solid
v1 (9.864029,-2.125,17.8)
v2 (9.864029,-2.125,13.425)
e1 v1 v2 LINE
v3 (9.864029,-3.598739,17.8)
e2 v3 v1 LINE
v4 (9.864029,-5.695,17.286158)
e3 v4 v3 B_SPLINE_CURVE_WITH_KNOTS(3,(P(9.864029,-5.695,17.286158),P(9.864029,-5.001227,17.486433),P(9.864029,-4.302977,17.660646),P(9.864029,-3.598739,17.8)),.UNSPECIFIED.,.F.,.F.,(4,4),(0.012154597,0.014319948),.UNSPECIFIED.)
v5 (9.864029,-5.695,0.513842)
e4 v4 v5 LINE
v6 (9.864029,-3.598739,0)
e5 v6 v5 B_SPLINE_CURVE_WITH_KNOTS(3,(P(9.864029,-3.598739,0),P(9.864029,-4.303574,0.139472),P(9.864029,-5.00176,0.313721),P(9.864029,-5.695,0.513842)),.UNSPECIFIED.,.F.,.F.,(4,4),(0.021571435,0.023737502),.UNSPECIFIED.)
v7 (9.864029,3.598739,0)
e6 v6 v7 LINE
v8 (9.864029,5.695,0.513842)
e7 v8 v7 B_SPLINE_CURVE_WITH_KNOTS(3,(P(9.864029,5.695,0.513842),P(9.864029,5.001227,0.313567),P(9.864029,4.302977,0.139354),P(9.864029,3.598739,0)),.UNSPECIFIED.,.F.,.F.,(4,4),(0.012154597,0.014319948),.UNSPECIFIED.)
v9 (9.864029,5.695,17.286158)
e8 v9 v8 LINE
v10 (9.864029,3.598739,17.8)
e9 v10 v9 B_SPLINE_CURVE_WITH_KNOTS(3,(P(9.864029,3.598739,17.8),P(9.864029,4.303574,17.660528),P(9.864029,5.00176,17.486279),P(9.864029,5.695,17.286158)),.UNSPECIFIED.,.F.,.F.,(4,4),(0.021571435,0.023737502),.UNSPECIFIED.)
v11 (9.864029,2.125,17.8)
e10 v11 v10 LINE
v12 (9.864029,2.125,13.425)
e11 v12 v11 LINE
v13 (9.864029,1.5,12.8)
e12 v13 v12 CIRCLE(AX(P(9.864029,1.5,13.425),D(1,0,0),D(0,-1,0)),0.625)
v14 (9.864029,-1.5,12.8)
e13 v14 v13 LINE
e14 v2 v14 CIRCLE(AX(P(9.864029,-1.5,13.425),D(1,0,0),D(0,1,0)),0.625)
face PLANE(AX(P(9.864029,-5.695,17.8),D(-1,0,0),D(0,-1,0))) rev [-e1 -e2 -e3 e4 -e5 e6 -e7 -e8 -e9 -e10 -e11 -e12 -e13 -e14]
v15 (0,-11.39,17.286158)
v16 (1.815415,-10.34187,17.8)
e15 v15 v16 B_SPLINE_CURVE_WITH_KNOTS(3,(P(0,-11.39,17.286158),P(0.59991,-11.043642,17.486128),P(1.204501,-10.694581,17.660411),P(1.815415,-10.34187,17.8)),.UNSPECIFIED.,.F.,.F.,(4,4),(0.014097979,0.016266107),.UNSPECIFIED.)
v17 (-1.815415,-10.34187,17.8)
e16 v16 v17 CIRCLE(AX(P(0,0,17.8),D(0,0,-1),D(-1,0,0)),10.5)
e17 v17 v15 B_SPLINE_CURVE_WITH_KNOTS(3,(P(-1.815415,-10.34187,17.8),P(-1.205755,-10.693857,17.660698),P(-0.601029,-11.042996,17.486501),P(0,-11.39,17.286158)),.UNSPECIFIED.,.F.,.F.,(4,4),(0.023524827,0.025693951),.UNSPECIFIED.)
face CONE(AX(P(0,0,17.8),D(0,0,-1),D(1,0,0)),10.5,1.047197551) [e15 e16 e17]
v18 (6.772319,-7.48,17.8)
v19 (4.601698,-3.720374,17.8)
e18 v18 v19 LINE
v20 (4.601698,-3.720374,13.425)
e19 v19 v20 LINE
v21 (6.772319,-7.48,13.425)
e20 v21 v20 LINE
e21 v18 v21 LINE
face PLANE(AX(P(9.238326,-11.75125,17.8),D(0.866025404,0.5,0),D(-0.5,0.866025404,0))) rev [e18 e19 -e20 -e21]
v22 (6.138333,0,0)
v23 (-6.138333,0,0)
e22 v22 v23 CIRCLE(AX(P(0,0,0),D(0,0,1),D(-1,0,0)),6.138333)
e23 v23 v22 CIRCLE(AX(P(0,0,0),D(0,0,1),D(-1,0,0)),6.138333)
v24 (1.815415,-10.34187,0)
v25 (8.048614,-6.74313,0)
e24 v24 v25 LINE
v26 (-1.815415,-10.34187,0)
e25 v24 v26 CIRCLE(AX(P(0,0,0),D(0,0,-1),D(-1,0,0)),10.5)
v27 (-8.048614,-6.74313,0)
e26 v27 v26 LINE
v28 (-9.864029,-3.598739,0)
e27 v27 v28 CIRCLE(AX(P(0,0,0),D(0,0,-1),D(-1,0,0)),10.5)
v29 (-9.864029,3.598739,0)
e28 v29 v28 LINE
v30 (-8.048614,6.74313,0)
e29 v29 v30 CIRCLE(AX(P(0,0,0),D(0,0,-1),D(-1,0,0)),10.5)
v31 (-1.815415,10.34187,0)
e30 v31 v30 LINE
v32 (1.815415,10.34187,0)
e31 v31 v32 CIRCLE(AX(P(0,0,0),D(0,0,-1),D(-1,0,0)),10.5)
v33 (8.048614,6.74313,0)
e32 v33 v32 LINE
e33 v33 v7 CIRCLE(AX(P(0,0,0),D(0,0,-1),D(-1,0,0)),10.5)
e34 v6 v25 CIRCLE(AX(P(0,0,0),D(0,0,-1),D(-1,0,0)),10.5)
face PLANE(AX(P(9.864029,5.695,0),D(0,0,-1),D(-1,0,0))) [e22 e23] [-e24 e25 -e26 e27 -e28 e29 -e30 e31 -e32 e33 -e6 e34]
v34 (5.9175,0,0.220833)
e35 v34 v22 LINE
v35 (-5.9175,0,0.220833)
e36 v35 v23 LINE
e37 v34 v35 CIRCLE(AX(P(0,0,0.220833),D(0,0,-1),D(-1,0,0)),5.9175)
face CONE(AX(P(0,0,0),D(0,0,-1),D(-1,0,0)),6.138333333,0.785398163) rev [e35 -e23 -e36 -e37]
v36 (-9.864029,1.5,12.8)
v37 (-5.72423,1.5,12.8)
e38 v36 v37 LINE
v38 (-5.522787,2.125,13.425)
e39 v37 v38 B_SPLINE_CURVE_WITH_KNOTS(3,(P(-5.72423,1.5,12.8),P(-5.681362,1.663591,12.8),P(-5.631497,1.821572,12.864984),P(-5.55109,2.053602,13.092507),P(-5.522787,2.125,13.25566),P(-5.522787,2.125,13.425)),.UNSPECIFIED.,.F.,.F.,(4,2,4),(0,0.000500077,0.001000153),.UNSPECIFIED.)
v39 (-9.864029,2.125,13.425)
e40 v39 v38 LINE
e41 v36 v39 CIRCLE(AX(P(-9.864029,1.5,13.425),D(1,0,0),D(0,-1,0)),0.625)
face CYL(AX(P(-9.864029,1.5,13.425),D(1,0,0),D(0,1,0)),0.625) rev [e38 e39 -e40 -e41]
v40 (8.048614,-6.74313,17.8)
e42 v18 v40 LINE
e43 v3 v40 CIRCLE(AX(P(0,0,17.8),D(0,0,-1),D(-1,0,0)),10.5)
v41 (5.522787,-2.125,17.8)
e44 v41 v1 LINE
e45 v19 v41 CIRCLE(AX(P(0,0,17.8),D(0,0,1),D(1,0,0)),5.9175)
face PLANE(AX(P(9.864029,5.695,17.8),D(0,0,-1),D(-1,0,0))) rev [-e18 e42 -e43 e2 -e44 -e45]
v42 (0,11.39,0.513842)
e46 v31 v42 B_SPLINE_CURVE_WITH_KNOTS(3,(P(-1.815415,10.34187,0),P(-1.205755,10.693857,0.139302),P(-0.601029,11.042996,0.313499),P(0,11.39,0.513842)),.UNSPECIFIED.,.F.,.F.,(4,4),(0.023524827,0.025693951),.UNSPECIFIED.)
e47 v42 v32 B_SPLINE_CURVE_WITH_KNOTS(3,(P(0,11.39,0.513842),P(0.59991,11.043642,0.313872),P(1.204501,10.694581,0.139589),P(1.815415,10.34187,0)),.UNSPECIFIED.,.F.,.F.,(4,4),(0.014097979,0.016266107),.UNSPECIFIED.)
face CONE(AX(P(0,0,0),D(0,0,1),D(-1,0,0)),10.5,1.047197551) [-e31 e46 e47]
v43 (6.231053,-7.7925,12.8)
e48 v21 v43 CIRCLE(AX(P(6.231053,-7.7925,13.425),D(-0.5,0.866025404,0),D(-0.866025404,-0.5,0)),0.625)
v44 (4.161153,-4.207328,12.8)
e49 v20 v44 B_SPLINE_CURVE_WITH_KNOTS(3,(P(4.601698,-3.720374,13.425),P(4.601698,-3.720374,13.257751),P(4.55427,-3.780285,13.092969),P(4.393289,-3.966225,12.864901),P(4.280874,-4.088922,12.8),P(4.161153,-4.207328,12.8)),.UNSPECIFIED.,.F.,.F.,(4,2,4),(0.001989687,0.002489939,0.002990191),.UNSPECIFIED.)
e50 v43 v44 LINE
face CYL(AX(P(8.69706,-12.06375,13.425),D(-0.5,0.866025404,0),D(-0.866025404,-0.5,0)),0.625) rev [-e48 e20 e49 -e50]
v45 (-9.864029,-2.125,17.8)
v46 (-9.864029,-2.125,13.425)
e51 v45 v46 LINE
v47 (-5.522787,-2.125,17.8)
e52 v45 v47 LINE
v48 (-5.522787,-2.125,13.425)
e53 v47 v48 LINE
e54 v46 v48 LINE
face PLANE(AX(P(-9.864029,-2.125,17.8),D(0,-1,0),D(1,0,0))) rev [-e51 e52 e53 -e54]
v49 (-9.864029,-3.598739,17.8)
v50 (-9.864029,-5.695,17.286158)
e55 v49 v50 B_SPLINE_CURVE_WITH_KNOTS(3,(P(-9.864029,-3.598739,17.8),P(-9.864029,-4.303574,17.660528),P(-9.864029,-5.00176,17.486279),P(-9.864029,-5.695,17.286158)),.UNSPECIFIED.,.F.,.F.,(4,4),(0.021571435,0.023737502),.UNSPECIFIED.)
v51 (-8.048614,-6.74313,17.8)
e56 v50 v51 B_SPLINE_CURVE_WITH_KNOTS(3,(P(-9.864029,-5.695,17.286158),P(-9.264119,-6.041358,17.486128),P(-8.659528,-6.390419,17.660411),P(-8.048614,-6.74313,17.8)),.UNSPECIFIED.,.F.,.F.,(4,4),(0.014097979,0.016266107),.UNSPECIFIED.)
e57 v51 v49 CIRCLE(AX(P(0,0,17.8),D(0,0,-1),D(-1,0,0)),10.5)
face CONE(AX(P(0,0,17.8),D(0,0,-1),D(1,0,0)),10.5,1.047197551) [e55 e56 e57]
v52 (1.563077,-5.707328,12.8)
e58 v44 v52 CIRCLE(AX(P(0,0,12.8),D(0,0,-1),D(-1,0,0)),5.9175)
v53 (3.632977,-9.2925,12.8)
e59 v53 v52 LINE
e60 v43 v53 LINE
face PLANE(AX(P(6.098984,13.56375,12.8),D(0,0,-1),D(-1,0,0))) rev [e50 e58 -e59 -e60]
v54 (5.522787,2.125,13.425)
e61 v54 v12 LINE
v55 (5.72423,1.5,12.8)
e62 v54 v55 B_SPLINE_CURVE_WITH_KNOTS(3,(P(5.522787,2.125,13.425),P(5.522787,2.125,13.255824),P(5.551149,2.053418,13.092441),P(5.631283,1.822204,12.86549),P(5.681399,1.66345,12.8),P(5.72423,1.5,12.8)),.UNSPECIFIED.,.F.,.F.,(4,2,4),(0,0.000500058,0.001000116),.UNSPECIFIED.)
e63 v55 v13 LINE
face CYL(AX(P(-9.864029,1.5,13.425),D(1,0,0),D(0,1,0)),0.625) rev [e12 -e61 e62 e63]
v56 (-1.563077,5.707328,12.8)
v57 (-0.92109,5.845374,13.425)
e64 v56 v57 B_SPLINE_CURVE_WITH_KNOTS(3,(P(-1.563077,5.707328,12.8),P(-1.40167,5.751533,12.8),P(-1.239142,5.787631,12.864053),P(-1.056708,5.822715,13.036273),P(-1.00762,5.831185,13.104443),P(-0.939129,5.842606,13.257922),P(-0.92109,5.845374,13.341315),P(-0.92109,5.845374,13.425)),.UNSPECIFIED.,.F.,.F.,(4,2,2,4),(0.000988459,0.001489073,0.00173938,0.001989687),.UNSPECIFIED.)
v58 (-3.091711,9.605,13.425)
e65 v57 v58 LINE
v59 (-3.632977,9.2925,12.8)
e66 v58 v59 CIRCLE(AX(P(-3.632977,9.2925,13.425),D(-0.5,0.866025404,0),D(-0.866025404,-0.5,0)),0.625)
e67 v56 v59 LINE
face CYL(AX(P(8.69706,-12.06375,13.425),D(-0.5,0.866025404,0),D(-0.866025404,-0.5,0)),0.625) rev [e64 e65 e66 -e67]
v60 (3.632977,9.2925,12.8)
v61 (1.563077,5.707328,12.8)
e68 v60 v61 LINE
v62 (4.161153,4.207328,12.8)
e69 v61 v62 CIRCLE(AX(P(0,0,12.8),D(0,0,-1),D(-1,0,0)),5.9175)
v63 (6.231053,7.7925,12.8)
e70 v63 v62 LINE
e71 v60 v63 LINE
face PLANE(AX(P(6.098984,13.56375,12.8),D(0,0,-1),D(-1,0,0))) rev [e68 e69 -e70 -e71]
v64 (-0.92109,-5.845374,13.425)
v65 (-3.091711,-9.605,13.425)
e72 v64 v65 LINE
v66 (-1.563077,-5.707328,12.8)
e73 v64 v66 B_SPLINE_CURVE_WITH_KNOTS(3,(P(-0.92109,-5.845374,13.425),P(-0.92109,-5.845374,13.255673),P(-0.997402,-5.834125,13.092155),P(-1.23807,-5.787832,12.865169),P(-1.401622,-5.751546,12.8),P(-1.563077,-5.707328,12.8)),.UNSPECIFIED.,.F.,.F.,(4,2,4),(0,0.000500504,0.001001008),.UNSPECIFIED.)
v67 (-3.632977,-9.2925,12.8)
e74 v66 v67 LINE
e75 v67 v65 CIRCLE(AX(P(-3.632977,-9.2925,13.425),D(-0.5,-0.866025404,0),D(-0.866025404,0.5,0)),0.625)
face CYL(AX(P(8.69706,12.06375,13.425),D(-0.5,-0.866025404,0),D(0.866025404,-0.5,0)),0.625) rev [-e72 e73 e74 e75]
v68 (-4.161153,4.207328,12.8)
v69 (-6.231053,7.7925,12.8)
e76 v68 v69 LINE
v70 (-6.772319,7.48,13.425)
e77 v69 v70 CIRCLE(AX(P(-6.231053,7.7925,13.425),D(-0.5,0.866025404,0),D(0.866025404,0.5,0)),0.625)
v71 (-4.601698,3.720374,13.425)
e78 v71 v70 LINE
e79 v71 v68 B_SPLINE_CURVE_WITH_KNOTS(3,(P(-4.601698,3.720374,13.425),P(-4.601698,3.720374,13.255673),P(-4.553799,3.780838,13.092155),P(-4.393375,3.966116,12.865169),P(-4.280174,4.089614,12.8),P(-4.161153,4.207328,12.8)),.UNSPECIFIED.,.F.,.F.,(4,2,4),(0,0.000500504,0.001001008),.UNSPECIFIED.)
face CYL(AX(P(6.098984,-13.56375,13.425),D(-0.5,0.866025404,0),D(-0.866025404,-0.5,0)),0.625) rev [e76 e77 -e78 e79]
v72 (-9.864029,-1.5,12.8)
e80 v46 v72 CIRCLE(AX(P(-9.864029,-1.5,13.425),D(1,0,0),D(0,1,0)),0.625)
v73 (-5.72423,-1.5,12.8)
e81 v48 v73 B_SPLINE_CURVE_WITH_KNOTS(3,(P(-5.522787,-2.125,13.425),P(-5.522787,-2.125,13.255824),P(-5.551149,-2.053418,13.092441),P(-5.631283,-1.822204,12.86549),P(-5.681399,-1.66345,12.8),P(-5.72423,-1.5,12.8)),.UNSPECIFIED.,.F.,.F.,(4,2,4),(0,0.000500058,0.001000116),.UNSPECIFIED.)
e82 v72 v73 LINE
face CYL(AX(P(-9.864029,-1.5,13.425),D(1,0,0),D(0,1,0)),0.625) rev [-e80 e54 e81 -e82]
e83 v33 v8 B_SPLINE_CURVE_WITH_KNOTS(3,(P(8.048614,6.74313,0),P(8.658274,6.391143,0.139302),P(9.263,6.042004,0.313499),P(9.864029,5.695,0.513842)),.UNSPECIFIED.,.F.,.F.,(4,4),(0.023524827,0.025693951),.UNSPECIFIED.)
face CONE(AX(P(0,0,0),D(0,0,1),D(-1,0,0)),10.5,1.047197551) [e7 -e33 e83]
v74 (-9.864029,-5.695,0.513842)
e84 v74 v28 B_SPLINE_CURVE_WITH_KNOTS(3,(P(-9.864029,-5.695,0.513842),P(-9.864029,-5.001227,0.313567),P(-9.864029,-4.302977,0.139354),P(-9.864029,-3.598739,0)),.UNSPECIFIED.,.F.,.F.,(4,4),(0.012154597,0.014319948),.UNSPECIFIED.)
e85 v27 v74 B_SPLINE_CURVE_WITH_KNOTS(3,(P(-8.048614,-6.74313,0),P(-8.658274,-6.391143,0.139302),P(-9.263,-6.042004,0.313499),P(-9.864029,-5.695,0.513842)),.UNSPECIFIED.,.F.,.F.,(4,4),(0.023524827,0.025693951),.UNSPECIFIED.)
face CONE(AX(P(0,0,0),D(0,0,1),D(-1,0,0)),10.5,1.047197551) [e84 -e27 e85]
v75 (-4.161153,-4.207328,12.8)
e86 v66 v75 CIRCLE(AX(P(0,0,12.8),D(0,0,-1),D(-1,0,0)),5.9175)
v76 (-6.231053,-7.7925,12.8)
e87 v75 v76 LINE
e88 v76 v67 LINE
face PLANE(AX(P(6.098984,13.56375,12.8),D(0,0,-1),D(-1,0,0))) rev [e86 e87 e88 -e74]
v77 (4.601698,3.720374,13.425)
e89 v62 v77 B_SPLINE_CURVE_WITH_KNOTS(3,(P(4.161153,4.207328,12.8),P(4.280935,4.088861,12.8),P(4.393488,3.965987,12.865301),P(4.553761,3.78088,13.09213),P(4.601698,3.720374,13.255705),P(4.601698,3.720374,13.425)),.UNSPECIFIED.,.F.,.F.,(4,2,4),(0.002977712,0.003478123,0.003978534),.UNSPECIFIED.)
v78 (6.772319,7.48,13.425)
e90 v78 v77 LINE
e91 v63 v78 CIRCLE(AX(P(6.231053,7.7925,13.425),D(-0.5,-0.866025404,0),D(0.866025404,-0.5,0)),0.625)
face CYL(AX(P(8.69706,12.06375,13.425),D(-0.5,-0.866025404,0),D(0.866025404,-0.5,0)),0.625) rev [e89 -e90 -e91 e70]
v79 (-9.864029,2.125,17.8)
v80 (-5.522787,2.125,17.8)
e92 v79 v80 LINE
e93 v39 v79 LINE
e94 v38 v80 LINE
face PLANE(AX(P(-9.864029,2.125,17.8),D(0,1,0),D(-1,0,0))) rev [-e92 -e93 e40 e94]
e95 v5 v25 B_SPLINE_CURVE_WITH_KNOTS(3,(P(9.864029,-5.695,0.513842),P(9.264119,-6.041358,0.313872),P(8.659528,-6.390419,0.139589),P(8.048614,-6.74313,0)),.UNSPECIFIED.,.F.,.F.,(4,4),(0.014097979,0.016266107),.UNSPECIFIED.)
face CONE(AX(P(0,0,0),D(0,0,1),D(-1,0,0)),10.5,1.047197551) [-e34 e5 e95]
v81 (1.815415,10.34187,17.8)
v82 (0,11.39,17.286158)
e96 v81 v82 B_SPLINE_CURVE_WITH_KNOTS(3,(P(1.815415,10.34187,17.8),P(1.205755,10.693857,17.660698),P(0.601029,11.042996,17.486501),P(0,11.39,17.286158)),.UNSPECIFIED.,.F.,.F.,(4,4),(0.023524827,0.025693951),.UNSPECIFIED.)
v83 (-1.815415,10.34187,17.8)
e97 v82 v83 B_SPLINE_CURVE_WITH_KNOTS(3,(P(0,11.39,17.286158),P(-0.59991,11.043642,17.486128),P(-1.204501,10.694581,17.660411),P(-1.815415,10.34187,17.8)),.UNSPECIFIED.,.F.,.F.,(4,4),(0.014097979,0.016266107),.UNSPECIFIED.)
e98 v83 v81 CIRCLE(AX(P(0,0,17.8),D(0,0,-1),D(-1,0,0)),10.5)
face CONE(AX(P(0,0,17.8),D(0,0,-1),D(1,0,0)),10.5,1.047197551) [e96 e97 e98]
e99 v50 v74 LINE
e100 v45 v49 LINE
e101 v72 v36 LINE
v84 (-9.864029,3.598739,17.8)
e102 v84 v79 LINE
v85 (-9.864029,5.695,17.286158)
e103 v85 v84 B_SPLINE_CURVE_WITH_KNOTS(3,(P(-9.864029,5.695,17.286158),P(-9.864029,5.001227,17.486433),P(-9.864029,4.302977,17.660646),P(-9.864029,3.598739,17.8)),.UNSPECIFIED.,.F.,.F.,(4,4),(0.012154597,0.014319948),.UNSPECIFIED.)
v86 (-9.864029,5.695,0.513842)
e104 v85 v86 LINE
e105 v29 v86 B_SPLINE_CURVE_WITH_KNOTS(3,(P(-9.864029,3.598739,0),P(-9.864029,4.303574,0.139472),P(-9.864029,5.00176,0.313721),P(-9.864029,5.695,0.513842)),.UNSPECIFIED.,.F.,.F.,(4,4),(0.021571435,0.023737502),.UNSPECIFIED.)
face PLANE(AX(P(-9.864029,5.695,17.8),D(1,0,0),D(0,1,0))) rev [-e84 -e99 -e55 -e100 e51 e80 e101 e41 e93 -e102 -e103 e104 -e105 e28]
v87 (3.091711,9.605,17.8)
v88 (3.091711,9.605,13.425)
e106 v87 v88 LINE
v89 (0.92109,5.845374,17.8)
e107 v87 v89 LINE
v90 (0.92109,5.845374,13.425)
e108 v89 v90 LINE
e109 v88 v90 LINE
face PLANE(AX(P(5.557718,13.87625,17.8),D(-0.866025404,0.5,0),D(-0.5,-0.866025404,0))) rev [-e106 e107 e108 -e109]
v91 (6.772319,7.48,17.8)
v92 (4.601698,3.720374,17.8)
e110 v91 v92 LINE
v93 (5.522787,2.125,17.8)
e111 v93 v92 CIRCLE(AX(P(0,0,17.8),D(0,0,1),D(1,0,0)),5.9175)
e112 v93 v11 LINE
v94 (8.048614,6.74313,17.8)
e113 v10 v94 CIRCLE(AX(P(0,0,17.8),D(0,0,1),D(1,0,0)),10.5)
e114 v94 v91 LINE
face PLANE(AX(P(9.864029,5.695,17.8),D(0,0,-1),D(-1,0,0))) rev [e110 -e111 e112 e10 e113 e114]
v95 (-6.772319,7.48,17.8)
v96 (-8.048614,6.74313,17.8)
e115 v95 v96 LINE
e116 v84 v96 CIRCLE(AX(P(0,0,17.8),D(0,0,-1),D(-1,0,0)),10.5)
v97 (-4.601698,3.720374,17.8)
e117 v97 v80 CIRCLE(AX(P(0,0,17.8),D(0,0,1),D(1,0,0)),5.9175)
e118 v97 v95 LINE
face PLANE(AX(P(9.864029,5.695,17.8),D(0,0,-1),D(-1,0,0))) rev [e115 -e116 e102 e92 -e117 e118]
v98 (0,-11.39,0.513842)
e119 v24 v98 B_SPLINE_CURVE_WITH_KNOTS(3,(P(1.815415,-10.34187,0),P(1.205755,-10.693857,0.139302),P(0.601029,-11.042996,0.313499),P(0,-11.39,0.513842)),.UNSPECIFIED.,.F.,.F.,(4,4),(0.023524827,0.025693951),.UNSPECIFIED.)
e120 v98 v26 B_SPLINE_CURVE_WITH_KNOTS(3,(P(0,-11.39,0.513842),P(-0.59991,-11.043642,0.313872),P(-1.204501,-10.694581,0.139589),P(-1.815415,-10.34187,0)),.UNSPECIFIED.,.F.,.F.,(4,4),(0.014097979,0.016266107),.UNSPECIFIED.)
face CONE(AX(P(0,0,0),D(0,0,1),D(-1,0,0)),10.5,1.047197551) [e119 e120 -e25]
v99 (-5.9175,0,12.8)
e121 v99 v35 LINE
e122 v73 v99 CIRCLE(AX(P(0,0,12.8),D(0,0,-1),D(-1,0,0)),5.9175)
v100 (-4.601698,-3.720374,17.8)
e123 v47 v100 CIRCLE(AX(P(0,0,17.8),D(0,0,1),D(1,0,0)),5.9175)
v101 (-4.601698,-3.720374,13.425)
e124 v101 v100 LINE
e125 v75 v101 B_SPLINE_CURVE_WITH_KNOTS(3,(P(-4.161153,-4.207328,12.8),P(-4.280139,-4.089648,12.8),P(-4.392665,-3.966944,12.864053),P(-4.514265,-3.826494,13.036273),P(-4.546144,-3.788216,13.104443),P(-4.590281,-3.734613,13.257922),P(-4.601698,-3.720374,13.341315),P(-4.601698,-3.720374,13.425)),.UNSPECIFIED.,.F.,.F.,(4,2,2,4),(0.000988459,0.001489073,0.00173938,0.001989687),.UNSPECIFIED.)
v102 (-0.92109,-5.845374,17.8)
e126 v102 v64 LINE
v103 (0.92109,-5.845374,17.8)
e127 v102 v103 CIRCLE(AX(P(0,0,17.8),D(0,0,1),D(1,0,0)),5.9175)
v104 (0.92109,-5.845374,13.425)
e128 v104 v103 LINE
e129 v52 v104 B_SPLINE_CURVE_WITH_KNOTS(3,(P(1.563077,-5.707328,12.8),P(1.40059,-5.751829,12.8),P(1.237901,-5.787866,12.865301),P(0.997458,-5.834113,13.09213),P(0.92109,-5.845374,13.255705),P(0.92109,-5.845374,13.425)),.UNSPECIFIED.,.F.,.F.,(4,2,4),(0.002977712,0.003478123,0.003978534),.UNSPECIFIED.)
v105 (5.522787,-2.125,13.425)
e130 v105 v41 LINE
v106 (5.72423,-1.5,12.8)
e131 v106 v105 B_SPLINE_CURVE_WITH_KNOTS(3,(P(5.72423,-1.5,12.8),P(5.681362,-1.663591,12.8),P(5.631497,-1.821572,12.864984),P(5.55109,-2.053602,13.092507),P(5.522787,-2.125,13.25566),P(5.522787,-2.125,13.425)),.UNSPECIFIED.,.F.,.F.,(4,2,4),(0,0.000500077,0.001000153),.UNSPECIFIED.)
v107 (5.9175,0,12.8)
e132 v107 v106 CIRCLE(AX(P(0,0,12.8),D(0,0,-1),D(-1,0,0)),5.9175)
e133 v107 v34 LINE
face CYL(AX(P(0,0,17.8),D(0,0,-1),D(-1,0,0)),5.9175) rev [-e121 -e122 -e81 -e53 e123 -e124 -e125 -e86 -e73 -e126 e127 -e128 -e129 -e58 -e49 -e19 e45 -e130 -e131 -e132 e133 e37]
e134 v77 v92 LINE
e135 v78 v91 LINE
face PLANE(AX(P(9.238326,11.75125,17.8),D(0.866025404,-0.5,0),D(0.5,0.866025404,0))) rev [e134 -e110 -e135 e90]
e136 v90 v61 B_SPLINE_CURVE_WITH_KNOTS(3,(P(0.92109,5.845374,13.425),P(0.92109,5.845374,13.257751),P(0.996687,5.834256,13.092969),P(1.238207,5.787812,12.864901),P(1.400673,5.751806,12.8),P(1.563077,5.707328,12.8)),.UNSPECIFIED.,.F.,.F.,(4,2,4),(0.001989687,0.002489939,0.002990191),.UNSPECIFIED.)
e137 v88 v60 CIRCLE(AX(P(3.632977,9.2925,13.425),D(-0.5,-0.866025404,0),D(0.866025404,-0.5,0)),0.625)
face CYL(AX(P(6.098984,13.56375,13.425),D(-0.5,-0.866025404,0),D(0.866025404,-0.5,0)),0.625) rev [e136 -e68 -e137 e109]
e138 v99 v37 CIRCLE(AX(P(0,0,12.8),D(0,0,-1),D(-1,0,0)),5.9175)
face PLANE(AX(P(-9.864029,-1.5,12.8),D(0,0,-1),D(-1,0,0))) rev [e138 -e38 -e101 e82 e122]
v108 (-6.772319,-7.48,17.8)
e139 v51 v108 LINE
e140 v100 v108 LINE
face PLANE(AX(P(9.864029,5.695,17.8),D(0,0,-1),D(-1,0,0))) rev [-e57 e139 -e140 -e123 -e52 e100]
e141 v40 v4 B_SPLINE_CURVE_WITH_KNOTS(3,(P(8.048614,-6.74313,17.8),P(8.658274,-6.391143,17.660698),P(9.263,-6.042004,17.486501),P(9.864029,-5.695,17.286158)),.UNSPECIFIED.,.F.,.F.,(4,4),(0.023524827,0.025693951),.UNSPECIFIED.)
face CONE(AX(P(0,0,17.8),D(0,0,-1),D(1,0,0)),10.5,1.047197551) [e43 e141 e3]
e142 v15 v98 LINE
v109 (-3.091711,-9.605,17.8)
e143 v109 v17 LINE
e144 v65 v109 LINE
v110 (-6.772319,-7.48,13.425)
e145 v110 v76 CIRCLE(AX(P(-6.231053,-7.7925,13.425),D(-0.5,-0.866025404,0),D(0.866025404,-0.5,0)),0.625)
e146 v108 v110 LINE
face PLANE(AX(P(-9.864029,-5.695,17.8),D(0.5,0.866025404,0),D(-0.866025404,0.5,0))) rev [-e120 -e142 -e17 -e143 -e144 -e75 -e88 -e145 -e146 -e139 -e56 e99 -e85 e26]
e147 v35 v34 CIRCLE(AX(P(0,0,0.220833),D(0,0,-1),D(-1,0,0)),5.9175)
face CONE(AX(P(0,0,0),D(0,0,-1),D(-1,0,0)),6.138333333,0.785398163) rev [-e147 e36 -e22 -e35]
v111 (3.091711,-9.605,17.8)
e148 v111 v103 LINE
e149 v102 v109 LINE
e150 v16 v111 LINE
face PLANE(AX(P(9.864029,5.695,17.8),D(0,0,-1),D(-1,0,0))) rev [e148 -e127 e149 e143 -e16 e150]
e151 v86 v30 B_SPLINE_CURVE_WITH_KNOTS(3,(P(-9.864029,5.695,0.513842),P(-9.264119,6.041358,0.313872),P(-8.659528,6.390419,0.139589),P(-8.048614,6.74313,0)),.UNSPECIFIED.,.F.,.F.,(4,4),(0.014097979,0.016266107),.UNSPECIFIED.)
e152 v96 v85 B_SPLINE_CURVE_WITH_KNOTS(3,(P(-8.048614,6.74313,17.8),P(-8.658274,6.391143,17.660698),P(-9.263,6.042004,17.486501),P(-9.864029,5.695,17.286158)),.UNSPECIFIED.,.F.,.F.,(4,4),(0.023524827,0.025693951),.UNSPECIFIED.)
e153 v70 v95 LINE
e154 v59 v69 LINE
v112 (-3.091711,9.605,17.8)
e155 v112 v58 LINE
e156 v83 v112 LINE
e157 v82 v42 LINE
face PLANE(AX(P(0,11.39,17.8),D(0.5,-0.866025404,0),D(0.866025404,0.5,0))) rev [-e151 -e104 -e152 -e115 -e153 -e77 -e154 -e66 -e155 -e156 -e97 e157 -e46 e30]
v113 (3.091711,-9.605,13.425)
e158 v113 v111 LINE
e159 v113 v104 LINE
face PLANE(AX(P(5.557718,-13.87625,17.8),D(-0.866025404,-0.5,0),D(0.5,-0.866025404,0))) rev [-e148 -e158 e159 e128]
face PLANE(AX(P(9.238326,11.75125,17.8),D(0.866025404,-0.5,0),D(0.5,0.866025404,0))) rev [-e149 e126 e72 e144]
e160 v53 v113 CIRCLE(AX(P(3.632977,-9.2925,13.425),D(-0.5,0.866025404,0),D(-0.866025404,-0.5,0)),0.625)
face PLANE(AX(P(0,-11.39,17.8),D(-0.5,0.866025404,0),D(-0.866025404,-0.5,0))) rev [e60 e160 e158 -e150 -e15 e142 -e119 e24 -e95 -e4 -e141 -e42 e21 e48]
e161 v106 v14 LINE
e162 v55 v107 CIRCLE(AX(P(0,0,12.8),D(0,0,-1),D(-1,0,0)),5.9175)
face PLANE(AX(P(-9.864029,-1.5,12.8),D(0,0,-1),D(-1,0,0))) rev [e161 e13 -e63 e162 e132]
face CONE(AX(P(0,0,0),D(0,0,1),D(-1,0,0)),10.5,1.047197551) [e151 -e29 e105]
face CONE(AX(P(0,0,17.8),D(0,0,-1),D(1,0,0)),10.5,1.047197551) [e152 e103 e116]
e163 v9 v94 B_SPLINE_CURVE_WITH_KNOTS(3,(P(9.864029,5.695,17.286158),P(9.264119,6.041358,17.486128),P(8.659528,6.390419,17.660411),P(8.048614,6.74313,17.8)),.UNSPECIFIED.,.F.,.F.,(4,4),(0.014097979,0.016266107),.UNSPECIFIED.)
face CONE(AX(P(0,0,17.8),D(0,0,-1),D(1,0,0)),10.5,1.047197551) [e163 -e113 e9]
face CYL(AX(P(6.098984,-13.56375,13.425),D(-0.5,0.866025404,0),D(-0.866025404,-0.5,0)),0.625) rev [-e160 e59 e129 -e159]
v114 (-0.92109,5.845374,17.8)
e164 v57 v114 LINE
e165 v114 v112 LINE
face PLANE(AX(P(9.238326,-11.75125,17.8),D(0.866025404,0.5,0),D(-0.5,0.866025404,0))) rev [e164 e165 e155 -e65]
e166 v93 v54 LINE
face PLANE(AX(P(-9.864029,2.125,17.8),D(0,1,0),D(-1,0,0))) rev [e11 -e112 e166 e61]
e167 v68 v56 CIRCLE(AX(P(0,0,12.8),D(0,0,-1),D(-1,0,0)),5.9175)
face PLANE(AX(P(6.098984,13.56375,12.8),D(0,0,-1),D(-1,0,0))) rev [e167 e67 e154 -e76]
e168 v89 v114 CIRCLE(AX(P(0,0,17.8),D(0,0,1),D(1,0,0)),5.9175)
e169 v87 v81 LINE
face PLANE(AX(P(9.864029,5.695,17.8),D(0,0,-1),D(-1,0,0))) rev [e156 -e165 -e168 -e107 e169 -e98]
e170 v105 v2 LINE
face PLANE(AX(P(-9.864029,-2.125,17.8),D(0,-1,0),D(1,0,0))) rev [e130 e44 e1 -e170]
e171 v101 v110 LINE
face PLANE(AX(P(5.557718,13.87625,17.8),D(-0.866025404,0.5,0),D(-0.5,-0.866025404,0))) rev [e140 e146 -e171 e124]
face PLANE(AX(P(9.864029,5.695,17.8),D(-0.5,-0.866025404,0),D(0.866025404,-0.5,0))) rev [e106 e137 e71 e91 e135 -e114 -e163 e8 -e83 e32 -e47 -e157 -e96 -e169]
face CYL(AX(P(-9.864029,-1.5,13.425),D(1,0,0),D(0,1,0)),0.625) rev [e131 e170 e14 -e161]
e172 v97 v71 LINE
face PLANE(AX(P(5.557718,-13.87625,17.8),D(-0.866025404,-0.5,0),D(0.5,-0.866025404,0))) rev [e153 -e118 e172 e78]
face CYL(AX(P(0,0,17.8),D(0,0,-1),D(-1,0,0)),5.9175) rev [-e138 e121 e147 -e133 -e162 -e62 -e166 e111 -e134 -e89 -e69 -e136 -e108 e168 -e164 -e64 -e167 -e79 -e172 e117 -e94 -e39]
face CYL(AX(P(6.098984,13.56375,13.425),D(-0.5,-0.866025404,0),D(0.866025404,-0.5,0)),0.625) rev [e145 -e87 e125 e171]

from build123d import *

# Parameters (mm, degrees)
SKETCH1_R          = 5.9175
BASE_EXTRUDE_DEPTH = 17.8
SKETCH2_OUTSIDE_W  = 112.978
SKETCH2_OUTSIDE_H  = 116.03
SKETCH2_OUTSIDE_R  = 10.5
CUT_EXTRUDE1_DEPTH = 24.321045753
CUT_EXTRUDE1_DRAFT = -60
SKETCH3_OUTSIDE_W  = 112.978
SKETCH3_OUTSIDE_H  = 116.03
SKETCH3_OUTSIDE_R  = 10.5
CUT_EXTRUDE2_DEPTH = 24.321045753
CUT_EXTRUDE2_DRAFT = -60
CUT_EXTRUDE3_DEPTH = 29.909659285
CIRPATTERN1_COUNT  = 3
CHAMFER1_SIZE      = 0.220833333


with BuildPart() as part:
    # Sketch1 → Base-Extrude (new body)
    with BuildSketch(Plane.XY):
        Polygon((0, 11.39), (-9.864029349, 5.695), (-9.864029349, -5.695), (0, -11.39), (9.864029349, -5.695), (9.864029349, 5.695), align=None)
        Circle(SKETCH1_R, mode=Mode.SUBTRACT)
    extrude(amount=BASE_EXTRUDE_DEPTH)


with BuildPart() as cut_extrude1_tool:
    # Sketch2 outside → Cut-Extrude1 (with draft: the straight prism first)
    with BuildSketch(Plane(origin=(0, 0, 0), x_dir=(-1, 0, 0), z_dir=(0, 0, -1))):
        Rectangle(SKETCH2_OUTSIDE_W, SKETCH2_OUTSIDE_H)
        Circle(SKETCH2_OUTSIDE_R, mode=Mode.SUBTRACT)
    extrude(amount=-CUT_EXTRUDE1_DEPTH)
    # Cut-Extrude1: the draft: its side faces are tilted about the plane it starts from
    cut_extrude1_sides = [cut_extrude1_tool.faces().sort_by_distance(p)[0] for p in [
        (0, -58.015, 12.160522876),
        (-56.489, 0, 12.160522876),
        (0, 58.015, 12.160522876),
        (56.489, 0, 12.160522876),
        (10.5, 0, 12.160522876),
    ]]
    draft(cut_extrude1_sides, Plane(origin=(0, 0, 0), x_dir=(-1, 0, 0), z_dir=(0, 0, -1)), CUT_EXTRUDE1_DRAFT)


with BuildPart() as part_1:
    add(part.part)

    # Cut-Extrude1: cut by cut_extrude1_tool
    add(cut_extrude1_tool.part, mode=Mode.SUBTRACT)


with BuildPart() as cut_extrude2_tool:
    # Sketch3 outside → Cut-Extrude2 (with draft: the straight prism first)
    with BuildSketch(Plane.XY.offset(17.8)):
        Rectangle(SKETCH3_OUTSIDE_W, SKETCH3_OUTSIDE_H)
        Circle(SKETCH3_OUTSIDE_R, mode=Mode.SUBTRACT)
    extrude(amount=-CUT_EXTRUDE2_DEPTH)
    # Cut-Extrude2: the draft: its side faces are tilted about the plane it starts from
    cut_extrude2_sides = [cut_extrude2_tool.faces().sort_by_distance(p)[0] for p in [
        (0, -58.015, 5.639477124),
        (56.489, 0, 5.639477124),
        (0, 58.015, 5.639477124),
        (-56.489, 0, 5.639477124),
        (-10.5, 0, 5.639477124),
    ]]
    draft(cut_extrude2_sides, Plane.XY.offset(17.8), CUT_EXTRUDE2_DRAFT)


with BuildPart() as part_2:
    add(part_1.part)

    # Cut-Extrude2: cut by cut_extrude2_tool
    add(cut_extrude2_tool.part, mode=Mode.SUBTRACT)

    # Sketch6 → Cut-Extrude3 (cut, through all)
    with BuildSketch(Plane(origin=(9.864029349, 0, 0), x_dir=(0, 0, -1), z_dir=(1, 0, 0))):
        with BuildLine():
            Line((-17.8, -2.125), (-17.8, 2.125))
            Line((-17.8, 2.125), (-13.425, 2.125))
            ThreePointArc((-13.425, 2.125), (-12.983058262, 1.941941738), (-12.8, 1.5))
            Line((-12.8, 1.5), (-12.8, -1.5))
            ThreePointArc((-12.8, -1.5), (-12.983058262, -1.941941738), (-13.425, -2.125))
            Line((-13.425, -2.125), (-17.8, -2.125))
        make_face()
    cut_extrude3 = extrude(amount=-CUT_EXTRUDE3_DEPTH, mode=Mode.SUBTRACT)

    # CirPattern1: Cut-Extrude3 ×3 about axis
    cirpattern1_axis = Axis((0, 0, 0), (0, 0, 1))
    for i in range(1, CIRPATTERN1_COUNT):
        add(cut_extrude3.rotate(cirpattern1_axis, i * 360 / CIRPATTERN1_COUNT), mode=Mode.SUBTRACT)

    # Chamfer1
    chamfer1_edges = [part_2.edges().sort_by_distance(p)[0] for p in [
        (-5.9175, 0, 0),
    ]]
    chamfer(chamfer1_edges, length=CHAMFER1_SIZE)


solid = part_2.part
